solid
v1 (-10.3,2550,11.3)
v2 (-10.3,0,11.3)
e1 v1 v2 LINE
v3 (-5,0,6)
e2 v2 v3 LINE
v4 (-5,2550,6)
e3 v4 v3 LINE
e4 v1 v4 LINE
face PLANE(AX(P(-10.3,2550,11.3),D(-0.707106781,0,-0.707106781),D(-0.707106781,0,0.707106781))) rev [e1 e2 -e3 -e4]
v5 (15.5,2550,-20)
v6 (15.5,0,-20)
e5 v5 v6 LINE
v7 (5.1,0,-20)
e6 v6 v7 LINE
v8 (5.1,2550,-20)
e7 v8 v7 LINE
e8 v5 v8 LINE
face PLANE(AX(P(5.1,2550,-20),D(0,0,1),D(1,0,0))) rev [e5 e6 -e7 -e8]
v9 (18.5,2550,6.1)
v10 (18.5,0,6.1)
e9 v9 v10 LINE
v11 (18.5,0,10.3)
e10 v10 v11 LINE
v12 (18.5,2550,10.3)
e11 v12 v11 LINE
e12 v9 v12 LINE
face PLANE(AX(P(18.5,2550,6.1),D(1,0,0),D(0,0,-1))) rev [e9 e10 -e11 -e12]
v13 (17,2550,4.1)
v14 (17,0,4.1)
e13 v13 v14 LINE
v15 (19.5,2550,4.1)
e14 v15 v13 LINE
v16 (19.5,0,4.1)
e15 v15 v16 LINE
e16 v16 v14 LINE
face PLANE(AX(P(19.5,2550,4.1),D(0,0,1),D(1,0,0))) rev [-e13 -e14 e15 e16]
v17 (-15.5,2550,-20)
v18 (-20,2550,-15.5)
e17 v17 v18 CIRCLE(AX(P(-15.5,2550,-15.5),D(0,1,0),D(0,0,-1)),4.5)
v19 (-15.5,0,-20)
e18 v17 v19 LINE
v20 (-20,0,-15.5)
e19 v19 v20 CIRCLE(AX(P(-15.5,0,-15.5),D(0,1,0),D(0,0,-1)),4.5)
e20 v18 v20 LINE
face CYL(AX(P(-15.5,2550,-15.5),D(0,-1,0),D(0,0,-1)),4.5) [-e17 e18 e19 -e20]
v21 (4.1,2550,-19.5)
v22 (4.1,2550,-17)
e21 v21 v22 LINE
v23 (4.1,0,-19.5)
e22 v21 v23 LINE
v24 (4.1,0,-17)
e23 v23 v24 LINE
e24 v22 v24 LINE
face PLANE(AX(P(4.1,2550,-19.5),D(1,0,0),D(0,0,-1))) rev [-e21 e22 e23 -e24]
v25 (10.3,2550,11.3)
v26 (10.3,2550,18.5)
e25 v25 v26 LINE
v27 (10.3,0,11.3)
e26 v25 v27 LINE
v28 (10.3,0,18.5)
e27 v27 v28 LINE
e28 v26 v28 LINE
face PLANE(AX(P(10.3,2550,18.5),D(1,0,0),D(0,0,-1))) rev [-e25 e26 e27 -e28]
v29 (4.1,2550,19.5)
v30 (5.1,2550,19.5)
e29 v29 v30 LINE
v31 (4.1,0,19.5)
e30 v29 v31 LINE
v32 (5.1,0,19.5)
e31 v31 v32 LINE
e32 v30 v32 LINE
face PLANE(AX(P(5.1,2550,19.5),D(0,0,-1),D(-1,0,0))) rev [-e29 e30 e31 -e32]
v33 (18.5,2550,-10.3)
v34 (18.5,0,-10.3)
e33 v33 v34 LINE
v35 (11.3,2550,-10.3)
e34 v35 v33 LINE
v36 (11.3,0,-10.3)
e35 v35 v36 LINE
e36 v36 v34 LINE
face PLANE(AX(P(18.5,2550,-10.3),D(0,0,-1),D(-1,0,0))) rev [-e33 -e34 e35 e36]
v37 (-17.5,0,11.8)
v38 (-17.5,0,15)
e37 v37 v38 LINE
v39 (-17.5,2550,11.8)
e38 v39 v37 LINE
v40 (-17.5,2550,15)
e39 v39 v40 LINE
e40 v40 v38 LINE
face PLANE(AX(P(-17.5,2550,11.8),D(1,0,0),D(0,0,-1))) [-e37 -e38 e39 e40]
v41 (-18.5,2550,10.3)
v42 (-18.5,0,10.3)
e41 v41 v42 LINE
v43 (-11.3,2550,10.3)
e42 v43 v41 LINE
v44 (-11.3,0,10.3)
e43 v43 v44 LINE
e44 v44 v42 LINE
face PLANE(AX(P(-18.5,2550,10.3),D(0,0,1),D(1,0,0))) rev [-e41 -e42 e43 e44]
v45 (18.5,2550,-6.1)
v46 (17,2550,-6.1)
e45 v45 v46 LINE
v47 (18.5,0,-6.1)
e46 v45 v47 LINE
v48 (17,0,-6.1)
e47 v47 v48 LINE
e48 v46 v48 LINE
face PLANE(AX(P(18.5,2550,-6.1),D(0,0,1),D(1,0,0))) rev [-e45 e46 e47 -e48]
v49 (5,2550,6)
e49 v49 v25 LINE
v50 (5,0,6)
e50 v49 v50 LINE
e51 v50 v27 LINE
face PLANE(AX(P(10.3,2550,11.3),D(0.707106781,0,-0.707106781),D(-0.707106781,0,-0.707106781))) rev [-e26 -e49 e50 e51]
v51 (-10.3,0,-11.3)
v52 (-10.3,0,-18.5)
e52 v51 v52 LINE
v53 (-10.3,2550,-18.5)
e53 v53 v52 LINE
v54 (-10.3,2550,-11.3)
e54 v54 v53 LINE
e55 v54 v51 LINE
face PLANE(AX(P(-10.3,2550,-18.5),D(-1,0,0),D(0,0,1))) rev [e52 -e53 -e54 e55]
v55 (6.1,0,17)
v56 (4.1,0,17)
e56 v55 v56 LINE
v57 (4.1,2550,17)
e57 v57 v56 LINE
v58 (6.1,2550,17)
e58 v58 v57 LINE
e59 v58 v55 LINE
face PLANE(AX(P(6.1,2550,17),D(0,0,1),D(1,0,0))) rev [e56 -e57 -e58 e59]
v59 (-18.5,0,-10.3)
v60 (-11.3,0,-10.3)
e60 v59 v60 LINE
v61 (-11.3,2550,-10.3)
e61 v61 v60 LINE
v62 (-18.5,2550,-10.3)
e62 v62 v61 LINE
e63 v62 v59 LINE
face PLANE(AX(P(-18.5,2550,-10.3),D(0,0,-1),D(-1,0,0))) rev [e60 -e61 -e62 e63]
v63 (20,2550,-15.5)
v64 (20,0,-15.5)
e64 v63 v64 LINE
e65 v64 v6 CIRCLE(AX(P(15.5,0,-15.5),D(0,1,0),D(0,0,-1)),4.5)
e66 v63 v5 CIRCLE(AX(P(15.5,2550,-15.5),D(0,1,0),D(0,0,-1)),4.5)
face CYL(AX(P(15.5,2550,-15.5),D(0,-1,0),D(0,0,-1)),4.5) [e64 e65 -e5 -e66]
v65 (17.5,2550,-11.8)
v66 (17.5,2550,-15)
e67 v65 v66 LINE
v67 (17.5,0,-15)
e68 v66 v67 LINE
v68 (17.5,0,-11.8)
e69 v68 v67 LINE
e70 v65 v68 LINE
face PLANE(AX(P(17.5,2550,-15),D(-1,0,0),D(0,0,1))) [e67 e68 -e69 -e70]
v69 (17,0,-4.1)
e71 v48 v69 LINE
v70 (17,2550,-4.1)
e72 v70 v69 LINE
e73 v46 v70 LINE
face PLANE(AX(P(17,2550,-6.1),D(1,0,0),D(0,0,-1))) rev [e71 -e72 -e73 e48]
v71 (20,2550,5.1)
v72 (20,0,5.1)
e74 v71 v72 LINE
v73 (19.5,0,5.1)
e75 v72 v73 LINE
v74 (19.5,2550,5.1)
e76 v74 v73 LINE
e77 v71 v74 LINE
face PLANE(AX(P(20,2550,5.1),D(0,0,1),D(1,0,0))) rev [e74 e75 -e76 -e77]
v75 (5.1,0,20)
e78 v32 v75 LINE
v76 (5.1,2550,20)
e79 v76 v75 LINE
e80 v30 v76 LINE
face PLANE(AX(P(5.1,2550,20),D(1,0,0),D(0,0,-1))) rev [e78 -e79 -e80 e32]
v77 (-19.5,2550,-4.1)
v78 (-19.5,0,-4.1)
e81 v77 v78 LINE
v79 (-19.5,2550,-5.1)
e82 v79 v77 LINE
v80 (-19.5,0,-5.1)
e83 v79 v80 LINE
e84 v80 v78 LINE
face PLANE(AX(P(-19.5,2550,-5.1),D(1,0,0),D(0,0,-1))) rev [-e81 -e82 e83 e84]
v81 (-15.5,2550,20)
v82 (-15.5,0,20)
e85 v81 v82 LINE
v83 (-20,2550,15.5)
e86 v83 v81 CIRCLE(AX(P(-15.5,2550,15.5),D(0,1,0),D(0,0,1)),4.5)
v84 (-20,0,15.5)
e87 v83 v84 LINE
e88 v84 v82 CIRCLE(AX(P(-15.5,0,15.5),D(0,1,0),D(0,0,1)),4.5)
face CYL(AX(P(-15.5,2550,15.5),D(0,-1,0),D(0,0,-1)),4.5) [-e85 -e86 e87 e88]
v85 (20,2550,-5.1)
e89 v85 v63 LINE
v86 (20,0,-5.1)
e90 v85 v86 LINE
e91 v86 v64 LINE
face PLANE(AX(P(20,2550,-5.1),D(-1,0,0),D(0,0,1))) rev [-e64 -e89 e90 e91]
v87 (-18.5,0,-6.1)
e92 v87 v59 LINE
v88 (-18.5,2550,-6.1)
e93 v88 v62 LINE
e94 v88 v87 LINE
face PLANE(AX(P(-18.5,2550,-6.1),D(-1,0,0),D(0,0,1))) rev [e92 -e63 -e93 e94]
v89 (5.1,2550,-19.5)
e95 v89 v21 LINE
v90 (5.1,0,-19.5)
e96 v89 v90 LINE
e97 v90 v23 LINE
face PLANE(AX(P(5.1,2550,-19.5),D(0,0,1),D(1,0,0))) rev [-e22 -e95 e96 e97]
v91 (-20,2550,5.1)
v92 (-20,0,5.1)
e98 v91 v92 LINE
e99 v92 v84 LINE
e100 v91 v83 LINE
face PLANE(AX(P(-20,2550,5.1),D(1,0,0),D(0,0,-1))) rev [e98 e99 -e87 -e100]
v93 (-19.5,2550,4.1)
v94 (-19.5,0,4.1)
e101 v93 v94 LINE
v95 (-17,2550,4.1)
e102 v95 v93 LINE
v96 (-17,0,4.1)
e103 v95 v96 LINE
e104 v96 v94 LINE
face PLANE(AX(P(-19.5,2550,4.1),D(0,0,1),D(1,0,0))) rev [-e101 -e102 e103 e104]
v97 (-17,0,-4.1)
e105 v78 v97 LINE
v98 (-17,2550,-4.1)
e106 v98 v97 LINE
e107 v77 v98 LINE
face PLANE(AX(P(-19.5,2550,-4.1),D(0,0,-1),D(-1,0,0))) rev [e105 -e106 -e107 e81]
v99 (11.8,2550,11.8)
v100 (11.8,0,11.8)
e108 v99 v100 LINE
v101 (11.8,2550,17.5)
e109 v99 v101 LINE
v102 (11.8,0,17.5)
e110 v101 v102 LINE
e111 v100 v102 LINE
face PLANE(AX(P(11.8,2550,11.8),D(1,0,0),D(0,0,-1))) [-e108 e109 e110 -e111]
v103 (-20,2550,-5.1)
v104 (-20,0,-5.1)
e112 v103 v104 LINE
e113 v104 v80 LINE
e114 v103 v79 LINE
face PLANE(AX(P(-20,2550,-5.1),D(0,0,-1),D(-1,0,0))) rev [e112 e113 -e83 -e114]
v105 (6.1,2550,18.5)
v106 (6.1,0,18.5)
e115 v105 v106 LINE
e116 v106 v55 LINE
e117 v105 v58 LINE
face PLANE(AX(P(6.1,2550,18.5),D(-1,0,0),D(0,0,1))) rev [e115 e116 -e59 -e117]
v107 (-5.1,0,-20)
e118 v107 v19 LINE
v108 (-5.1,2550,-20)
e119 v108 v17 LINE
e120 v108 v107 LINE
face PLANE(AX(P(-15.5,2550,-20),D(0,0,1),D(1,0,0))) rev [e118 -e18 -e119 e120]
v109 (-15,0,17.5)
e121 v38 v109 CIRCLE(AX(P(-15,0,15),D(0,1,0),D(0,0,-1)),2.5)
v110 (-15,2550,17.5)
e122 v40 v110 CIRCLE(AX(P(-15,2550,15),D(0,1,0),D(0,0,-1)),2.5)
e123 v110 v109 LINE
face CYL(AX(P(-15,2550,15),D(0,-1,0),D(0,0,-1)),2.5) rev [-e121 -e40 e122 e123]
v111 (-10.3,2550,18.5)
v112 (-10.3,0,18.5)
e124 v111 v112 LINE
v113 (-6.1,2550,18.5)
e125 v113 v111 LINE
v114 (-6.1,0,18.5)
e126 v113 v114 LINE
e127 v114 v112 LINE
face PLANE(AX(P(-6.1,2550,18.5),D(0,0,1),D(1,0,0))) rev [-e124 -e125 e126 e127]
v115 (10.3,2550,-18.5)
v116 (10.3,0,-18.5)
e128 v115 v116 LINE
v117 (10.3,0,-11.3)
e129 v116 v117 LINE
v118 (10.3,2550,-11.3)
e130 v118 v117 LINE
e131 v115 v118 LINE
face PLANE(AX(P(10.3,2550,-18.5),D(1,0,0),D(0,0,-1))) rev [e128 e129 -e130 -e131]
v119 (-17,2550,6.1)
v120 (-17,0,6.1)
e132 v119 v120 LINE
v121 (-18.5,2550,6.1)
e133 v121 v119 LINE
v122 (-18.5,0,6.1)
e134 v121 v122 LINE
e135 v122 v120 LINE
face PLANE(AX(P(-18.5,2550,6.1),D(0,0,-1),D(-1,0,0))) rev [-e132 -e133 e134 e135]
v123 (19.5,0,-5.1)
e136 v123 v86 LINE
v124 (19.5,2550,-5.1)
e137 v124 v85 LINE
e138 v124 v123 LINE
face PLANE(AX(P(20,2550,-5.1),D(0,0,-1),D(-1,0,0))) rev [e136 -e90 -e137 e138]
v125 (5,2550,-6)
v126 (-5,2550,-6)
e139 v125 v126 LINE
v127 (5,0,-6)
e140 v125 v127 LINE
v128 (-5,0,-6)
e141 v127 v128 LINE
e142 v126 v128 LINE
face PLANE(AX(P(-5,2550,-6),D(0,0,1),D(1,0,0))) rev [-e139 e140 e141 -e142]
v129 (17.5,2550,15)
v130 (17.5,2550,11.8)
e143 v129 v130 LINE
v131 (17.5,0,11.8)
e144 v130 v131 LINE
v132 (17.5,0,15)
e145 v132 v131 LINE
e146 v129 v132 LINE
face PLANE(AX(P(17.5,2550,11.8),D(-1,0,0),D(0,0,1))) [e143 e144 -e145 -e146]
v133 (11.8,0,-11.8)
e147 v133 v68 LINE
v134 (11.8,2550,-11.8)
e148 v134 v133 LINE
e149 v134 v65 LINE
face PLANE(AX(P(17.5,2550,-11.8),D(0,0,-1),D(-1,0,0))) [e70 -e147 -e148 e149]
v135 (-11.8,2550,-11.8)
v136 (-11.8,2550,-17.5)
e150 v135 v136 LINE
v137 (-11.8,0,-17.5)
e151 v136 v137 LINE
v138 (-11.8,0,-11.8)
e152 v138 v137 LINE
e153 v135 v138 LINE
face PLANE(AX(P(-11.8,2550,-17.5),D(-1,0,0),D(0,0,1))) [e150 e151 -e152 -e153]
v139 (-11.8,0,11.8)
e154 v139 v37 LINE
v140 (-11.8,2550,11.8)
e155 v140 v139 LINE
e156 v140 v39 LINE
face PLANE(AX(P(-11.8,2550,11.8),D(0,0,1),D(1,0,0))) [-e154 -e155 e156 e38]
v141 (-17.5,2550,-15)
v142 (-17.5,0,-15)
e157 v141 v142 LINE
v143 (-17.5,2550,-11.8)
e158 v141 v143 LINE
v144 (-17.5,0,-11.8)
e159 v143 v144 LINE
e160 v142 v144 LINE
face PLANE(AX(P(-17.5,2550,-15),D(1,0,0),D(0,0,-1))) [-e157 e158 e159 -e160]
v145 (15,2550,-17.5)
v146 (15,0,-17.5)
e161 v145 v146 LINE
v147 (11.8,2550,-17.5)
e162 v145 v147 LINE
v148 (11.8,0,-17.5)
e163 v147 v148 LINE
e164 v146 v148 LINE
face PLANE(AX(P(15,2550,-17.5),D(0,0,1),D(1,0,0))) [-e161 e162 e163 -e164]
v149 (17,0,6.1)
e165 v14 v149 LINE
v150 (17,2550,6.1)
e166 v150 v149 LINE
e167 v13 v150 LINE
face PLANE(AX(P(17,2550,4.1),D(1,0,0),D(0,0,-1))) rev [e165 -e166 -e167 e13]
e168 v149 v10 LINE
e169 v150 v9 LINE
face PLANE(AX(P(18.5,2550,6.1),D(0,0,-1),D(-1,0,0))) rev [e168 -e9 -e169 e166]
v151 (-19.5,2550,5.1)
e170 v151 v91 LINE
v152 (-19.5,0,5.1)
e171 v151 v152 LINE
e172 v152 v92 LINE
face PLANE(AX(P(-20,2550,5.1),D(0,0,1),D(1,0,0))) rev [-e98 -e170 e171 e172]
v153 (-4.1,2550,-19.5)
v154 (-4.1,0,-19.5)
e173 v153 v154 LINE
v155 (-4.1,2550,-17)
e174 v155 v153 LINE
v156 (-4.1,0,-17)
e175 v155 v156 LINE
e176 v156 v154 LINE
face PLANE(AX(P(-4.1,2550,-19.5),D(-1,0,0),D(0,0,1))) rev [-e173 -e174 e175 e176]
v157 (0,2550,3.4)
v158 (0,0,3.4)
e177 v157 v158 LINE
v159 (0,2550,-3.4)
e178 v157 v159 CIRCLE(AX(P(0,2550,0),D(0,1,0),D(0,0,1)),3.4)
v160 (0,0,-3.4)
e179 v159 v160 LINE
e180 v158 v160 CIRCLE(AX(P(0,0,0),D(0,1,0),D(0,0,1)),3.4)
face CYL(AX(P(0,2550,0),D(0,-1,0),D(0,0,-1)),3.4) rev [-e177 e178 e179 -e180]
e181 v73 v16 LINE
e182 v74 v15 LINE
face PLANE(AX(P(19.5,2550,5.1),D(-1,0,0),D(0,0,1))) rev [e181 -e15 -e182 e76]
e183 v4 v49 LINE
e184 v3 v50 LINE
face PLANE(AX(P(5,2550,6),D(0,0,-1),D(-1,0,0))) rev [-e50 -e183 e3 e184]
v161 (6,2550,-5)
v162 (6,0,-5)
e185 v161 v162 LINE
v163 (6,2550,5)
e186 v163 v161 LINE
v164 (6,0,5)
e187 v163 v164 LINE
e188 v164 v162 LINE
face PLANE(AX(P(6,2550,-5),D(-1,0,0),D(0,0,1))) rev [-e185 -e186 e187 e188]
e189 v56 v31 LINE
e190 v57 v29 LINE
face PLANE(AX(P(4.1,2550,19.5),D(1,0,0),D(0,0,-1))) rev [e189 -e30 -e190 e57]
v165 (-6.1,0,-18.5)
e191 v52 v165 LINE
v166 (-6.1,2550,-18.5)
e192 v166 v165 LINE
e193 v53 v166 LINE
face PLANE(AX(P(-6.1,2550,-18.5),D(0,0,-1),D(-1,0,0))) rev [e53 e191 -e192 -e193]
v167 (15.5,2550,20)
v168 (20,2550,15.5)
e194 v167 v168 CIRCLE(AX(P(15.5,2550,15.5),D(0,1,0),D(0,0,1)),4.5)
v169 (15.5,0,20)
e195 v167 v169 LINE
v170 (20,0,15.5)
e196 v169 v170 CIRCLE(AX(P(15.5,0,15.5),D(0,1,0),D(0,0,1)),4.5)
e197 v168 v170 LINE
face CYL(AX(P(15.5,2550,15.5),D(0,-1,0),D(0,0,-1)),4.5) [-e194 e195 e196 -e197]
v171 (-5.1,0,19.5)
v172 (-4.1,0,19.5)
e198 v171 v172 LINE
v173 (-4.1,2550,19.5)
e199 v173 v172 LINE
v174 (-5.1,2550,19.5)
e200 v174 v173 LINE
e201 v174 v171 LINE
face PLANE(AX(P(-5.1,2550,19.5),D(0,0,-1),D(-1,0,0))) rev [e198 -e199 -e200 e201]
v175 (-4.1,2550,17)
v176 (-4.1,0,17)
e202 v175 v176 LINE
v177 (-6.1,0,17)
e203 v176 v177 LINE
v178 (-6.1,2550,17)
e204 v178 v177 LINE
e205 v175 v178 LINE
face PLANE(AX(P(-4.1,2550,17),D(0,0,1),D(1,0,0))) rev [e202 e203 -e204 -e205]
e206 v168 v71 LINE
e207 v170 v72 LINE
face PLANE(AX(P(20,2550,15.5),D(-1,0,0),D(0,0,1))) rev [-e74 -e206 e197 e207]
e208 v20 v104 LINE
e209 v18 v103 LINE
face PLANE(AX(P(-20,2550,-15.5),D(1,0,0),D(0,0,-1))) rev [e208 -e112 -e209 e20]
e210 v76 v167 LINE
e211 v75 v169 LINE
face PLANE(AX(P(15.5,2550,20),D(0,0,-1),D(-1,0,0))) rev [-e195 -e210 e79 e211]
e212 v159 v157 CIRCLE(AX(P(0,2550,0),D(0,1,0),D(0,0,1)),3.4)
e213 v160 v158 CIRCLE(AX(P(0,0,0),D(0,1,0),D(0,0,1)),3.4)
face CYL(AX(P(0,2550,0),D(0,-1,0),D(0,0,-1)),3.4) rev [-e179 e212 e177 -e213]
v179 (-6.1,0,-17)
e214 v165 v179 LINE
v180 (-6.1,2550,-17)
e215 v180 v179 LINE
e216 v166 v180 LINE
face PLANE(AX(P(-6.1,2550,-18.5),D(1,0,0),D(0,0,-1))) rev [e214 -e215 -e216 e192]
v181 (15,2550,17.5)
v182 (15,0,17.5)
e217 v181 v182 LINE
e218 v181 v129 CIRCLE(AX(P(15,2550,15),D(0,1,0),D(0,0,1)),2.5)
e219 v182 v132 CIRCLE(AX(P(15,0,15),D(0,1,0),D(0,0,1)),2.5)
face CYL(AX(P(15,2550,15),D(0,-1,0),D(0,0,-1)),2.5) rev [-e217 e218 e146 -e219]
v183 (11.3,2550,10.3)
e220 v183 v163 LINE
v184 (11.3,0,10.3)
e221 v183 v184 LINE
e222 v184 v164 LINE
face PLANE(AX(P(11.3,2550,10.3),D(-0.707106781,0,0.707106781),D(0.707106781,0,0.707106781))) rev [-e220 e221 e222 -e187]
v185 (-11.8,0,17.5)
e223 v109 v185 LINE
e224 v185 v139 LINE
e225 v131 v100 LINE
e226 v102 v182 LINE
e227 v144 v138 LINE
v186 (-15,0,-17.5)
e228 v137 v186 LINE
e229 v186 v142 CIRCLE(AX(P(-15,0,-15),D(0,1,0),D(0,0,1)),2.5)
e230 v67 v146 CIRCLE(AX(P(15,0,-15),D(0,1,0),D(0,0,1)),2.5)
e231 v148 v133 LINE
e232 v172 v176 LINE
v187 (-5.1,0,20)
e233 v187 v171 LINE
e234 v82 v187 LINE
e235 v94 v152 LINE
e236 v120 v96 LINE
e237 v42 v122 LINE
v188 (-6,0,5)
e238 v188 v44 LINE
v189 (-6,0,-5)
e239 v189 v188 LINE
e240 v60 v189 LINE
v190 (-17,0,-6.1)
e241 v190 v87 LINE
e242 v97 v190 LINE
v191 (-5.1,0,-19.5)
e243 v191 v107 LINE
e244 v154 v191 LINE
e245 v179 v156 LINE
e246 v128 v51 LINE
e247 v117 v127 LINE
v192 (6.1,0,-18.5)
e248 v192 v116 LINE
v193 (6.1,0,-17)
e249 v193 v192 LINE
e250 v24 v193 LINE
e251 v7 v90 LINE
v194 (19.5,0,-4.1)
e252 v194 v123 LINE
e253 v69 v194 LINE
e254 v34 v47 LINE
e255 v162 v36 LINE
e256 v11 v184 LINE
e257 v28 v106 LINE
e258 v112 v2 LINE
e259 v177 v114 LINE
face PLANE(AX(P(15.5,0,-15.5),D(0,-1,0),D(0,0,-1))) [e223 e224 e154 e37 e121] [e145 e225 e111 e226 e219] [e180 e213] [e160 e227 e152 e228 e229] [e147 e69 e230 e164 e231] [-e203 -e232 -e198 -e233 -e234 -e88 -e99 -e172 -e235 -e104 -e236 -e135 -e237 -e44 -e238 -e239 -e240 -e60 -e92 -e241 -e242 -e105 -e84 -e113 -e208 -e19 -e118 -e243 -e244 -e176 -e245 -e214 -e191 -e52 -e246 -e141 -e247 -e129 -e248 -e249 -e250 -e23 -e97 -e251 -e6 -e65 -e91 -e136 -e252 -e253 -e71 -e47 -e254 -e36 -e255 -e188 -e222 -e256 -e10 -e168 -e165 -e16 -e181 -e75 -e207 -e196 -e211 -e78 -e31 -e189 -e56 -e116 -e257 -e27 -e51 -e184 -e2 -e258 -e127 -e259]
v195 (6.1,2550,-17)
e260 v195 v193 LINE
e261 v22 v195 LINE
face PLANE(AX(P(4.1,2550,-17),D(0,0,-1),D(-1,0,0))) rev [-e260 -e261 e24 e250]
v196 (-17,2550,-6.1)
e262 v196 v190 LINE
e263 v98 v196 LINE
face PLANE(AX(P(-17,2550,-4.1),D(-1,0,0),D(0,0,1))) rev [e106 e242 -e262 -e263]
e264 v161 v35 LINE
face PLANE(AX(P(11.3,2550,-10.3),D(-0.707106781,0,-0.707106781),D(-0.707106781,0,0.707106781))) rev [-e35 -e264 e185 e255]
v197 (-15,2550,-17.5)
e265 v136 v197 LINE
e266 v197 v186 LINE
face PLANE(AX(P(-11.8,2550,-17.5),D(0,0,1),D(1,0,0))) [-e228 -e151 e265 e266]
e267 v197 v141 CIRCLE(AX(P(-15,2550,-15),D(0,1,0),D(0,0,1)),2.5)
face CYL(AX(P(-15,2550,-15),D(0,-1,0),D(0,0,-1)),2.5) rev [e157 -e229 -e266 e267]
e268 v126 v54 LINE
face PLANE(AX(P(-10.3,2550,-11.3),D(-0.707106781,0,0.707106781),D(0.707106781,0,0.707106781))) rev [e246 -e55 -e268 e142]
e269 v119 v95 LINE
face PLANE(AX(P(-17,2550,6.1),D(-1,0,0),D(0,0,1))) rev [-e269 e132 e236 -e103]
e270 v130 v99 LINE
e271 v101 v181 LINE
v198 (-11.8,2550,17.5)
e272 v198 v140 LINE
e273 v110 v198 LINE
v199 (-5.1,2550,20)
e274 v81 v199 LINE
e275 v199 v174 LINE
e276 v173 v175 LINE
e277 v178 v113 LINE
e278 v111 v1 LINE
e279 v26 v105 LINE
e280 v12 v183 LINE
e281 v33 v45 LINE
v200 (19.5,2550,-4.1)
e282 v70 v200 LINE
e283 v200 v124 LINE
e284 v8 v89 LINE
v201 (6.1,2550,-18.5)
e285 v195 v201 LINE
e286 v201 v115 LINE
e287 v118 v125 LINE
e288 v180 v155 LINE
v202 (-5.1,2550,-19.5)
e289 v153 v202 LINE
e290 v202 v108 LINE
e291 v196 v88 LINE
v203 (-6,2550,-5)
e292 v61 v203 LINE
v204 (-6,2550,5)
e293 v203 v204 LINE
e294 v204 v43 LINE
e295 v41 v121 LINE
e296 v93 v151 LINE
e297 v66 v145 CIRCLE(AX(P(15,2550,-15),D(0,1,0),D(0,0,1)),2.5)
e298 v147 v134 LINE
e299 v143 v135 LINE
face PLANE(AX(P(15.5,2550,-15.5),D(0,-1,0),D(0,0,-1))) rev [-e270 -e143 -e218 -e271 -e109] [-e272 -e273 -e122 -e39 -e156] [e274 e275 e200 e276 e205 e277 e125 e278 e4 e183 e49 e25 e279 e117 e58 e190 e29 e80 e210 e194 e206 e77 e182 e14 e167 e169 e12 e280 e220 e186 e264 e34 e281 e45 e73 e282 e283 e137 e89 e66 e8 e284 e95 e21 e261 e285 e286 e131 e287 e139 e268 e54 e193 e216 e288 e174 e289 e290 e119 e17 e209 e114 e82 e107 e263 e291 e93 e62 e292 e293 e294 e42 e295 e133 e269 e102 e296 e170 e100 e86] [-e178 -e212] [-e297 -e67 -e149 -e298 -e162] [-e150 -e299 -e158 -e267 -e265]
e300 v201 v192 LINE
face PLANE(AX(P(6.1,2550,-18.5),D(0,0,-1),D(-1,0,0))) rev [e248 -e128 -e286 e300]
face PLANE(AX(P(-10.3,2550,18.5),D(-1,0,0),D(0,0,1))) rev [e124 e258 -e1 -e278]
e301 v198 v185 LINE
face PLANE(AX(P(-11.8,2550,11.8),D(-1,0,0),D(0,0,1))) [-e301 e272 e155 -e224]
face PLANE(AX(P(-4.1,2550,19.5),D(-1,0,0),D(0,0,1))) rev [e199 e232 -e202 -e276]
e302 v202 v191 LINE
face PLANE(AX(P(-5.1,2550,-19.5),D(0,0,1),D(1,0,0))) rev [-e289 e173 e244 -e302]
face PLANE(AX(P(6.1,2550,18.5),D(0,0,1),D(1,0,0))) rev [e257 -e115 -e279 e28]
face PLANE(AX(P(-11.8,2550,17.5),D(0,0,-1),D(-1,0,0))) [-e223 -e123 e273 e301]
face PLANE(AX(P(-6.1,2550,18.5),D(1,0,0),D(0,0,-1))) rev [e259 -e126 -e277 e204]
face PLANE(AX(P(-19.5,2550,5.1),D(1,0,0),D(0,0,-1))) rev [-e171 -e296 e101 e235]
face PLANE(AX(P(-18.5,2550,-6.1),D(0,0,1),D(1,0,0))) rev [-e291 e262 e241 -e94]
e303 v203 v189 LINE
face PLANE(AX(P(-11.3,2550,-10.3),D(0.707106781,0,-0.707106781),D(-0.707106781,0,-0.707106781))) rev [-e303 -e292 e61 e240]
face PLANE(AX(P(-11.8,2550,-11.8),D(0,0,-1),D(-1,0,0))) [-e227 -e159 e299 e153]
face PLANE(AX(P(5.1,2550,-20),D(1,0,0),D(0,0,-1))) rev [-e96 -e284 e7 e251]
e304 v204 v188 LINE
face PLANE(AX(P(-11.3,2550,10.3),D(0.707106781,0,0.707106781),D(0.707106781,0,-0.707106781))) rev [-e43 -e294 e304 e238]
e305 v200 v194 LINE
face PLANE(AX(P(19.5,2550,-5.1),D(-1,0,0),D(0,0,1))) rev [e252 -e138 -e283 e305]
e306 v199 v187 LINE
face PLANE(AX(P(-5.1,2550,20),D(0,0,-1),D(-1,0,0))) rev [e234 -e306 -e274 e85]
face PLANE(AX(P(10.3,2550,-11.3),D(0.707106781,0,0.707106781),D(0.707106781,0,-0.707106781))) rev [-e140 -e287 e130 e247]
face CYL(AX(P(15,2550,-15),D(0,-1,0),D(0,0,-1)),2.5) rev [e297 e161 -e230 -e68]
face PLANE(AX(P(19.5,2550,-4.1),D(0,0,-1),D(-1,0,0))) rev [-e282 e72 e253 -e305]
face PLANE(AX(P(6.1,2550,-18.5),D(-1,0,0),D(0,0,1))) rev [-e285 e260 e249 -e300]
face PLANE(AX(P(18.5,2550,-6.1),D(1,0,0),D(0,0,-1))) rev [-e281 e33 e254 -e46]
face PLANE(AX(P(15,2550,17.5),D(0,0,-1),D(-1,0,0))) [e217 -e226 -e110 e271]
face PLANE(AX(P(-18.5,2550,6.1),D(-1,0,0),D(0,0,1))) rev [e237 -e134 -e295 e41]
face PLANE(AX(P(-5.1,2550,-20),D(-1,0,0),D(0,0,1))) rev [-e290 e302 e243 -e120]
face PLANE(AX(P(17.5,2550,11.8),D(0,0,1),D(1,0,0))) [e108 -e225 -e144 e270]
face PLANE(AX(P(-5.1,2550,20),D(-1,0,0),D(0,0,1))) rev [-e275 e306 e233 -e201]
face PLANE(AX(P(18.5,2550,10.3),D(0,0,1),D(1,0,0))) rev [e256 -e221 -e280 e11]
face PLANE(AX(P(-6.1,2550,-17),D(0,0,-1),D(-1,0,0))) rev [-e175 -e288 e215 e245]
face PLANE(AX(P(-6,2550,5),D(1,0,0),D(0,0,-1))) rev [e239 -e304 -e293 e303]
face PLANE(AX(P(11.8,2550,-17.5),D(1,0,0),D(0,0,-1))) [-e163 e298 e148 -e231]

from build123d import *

# Parameters (mm, degrees)
SKETCH1_R                 = 3.4
F_40_X_40L_X_R4_5_1_DEPTH = 2550


with BuildPart() as part:
    # Sketch1 → 铝型材 40 X 40L X R4.5(1) (new body)
    with BuildSketch(Plane.ZX):
        with BuildLine():
            Line((-5.1, 20), (-5.1, 19.5))
            Line((-5.1, 19.5), (-4.1, 19.5))
            Line((-4.1, 19.5), (-4.1, 17))
            Line((-4.1, 17), (-6.1, 17))
            Line((-6.1, 17), (-6.1, 18.5))
            Line((-6.1, 18.5), (-10.3, 18.5))
            Line((-10.3, 18.5), (-10.3, 11.3))
            Line((-10.3, 11.3), (-5, 6))
            Line((-5, 6), (5, 6))
            Line((5, 6), (10.3, 11.3))
            Line((10.3, 11.3), (10.3, 18.5))
            Line((10.3, 18.5), (6.1, 18.5))
            Line((6.1, 18.5), (6.1, 17))
            Line((6.1, 17), (4.1, 17))
            Line((4.1, 17), (4.1, 19.5))
            Line((4.1, 19.5), (5.1, 19.5))
            Line((5.1, 19.5), (5.1, 20))
            Line((5.1, 20), (15.5, 20))
            ThreePointArc((15.5, 20), (18.681980515, 18.681980515), (20, 15.5))
            Line((20, 15.5), (20, 5.1))
            Line((20, 5.1), (19.5, 5.1))
            Line((19.5, 5.1), (19.5, 4.1))
            Line((19.5, 4.1), (17, 4.1))
            Line((17, 4.1), (17, 6.1))
            Line((17, 6.1), (18.5, 6.1))
            Line((18.5, 6.1), (18.5, 10.3))
            Line((18.5, 10.3), (11.3, 10.3))
            Line((11.3, 10.3), (6, 5))
            Line((6, 5), (6, -5))
            Line((6, -5), (11.3, -10.3))
            Line((11.3, -10.3), (18.5, -10.3))
            Line((18.5, -10.3), (18.5, -6.1))
            Line((18.5, -6.1), (17, -6.1))
            Line((17, -6.1), (17, -4.1))
            Line((17, -4.1), (19.5, -4.1))
            Line((19.5, -4.1), (19.5, -5.1))
            Line((19.5, -5.1), (20, -5.1))
            Line((20, -5.1), (20, -15.5))
            ThreePointArc((20, -15.5), (18.681980515, -18.681980515), (15.5, -20))
            Line((15.5, -20), (5.1, -20))
            Line((5.1, -20), (5.1, -19.5))
            Line((5.1, -19.5), (4.1, -19.5))
            Line((4.1, -19.5), (4.1, -17))
            Line((4.1, -17), (6.1, -17))
            Line((6.1, -17), (6.1, -18.5))
            Line((6.1, -18.5), (10.3, -18.5))
            Line((10.3, -18.5), (10.3, -11.3))
            Line((10.3, -11.3), (5, -6))
            Line((5, -6), (-5, -6))
            Line((-5, -6), (-10.3, -11.3))
            Line((-10.3, -11.3), (-10.3, -18.5))
            Line((-10.3, -18.5), (-6.1, -18.5))
            Line((-6.1, -18.5), (-6.1, -17))
            Line((-6.1, -17), (-4.1, -17))
            Line((-4.1, -17), (-4.1, -19.5))
            Line((-4.1, -19.5), (-5.1, -19.5))
            Line((-5.1, -19.5), (-5.1, -20))
            Line((-5.1, -20), (-15.5, -20))
            ThreePointArc((-15.5, -20), (-18.681980515, -18.681980515), (-20, -15.5))
            Line((-20, -15.5), (-20, -5.1))
            Line((-20, -5.1), (-19.5, -5.1))
            Line((-19.5, -5.1), (-19.5, -4.1))
            Line((-19.5, -4.1), (-17, -4.1))
            Line((-17, -4.1), (-17, -6.1))
            Line((-17, -6.1), (-18.5, -6.1))
            Line((-18.5, -6.1), (-18.5, -10.3))
            Line((-18.5, -10.3), (-11.3, -10.3))
            Line((-11.3, -10.3), (-6, -5))
            Line((-6, -5), (-6, 5))
            Line((-6, 5), (-11.3, 10.3))
            Line((-11.3, 10.3), (-18.5, 10.3))
            Line((-18.5, 10.3), (-18.5, 6.1))
            Line((-18.5, 6.1), (-17, 6.1))
            Line((-17, 6.1), (-17, 4.1))
            Line((-17, 4.1), (-19.5, 4.1))
            Line((-19.5, 4.1), (-19.5, 5.1))
            Line((-19.5, 5.1), (-20, 5.1))
            Line((-20, 5.1), (-20, 15.5))
            ThreePointArc((-20, 15.5), (-18.681980515, 18.681980515), (-15.5, 20))
            Line((-15.5, 20), (-5.1, 20))
        make_face()
        Circle(SKETCH1_R, mode=Mode.SUBTRACT)
        with BuildLine():
            Line((11.8, 17.5), (15, 17.5))
            ThreePointArc((15, 17.5), (16.767766953, 16.767766953), (17.5, 15))
            Line((17.5, 15), (17.5, 11.8))
            Line((17.5, 11.8), (11.8, 11.8))
            Line((11.8, 11.8), (11.8, 17.5))
        make_face(mode=Mode.SUBTRACT)
        with BuildLine():
            Line((-15, 17.5), (-11.8, 17.5))
            Line((-11.8, 17.5), (-11.8, 11.8))
            Line((-11.8, 11.8), (-17.5, 11.8))
            Line((-17.5, 11.8), (-17.5, 15))
            ThreePointArc((-17.5, 15), (-16.767766953, 16.767766953), (-15, 17.5))
        make_face(mode=Mode.SUBTRACT)
        with BuildLine():
            Line((-17.5, -11.8), (-11.8, -11.8))
            Line((-11.8, -11.8), (-11.8, -17.5))
            Line((-11.8, -17.5), (-15, -17.5))
            ThreePointArc((-15, -17.5), (-16.767766953, -16.767766953), (-17.5, -15))
            Line((-17.5, -15), (-17.5, -11.8))
        make_face(mode=Mode.SUBTRACT)
        with BuildLine():
            Line((11.8, -11.8), (17.5, -11.8))
            Line((17.5, -11.8), (17.5, -15))
            ThreePointArc((17.5, -15), (16.767766953, -16.767766953), (15, -17.5))
            Line((15, -17.5), (11.8, -17.5))
            Line((11.8, -17.5), (11.8, -11.8))
        make_face(mode=Mode.SUBTRACT)
    extrude(amount=F_40_X_40L_X_R4_5_1_DEPTH)


solid = part.part
